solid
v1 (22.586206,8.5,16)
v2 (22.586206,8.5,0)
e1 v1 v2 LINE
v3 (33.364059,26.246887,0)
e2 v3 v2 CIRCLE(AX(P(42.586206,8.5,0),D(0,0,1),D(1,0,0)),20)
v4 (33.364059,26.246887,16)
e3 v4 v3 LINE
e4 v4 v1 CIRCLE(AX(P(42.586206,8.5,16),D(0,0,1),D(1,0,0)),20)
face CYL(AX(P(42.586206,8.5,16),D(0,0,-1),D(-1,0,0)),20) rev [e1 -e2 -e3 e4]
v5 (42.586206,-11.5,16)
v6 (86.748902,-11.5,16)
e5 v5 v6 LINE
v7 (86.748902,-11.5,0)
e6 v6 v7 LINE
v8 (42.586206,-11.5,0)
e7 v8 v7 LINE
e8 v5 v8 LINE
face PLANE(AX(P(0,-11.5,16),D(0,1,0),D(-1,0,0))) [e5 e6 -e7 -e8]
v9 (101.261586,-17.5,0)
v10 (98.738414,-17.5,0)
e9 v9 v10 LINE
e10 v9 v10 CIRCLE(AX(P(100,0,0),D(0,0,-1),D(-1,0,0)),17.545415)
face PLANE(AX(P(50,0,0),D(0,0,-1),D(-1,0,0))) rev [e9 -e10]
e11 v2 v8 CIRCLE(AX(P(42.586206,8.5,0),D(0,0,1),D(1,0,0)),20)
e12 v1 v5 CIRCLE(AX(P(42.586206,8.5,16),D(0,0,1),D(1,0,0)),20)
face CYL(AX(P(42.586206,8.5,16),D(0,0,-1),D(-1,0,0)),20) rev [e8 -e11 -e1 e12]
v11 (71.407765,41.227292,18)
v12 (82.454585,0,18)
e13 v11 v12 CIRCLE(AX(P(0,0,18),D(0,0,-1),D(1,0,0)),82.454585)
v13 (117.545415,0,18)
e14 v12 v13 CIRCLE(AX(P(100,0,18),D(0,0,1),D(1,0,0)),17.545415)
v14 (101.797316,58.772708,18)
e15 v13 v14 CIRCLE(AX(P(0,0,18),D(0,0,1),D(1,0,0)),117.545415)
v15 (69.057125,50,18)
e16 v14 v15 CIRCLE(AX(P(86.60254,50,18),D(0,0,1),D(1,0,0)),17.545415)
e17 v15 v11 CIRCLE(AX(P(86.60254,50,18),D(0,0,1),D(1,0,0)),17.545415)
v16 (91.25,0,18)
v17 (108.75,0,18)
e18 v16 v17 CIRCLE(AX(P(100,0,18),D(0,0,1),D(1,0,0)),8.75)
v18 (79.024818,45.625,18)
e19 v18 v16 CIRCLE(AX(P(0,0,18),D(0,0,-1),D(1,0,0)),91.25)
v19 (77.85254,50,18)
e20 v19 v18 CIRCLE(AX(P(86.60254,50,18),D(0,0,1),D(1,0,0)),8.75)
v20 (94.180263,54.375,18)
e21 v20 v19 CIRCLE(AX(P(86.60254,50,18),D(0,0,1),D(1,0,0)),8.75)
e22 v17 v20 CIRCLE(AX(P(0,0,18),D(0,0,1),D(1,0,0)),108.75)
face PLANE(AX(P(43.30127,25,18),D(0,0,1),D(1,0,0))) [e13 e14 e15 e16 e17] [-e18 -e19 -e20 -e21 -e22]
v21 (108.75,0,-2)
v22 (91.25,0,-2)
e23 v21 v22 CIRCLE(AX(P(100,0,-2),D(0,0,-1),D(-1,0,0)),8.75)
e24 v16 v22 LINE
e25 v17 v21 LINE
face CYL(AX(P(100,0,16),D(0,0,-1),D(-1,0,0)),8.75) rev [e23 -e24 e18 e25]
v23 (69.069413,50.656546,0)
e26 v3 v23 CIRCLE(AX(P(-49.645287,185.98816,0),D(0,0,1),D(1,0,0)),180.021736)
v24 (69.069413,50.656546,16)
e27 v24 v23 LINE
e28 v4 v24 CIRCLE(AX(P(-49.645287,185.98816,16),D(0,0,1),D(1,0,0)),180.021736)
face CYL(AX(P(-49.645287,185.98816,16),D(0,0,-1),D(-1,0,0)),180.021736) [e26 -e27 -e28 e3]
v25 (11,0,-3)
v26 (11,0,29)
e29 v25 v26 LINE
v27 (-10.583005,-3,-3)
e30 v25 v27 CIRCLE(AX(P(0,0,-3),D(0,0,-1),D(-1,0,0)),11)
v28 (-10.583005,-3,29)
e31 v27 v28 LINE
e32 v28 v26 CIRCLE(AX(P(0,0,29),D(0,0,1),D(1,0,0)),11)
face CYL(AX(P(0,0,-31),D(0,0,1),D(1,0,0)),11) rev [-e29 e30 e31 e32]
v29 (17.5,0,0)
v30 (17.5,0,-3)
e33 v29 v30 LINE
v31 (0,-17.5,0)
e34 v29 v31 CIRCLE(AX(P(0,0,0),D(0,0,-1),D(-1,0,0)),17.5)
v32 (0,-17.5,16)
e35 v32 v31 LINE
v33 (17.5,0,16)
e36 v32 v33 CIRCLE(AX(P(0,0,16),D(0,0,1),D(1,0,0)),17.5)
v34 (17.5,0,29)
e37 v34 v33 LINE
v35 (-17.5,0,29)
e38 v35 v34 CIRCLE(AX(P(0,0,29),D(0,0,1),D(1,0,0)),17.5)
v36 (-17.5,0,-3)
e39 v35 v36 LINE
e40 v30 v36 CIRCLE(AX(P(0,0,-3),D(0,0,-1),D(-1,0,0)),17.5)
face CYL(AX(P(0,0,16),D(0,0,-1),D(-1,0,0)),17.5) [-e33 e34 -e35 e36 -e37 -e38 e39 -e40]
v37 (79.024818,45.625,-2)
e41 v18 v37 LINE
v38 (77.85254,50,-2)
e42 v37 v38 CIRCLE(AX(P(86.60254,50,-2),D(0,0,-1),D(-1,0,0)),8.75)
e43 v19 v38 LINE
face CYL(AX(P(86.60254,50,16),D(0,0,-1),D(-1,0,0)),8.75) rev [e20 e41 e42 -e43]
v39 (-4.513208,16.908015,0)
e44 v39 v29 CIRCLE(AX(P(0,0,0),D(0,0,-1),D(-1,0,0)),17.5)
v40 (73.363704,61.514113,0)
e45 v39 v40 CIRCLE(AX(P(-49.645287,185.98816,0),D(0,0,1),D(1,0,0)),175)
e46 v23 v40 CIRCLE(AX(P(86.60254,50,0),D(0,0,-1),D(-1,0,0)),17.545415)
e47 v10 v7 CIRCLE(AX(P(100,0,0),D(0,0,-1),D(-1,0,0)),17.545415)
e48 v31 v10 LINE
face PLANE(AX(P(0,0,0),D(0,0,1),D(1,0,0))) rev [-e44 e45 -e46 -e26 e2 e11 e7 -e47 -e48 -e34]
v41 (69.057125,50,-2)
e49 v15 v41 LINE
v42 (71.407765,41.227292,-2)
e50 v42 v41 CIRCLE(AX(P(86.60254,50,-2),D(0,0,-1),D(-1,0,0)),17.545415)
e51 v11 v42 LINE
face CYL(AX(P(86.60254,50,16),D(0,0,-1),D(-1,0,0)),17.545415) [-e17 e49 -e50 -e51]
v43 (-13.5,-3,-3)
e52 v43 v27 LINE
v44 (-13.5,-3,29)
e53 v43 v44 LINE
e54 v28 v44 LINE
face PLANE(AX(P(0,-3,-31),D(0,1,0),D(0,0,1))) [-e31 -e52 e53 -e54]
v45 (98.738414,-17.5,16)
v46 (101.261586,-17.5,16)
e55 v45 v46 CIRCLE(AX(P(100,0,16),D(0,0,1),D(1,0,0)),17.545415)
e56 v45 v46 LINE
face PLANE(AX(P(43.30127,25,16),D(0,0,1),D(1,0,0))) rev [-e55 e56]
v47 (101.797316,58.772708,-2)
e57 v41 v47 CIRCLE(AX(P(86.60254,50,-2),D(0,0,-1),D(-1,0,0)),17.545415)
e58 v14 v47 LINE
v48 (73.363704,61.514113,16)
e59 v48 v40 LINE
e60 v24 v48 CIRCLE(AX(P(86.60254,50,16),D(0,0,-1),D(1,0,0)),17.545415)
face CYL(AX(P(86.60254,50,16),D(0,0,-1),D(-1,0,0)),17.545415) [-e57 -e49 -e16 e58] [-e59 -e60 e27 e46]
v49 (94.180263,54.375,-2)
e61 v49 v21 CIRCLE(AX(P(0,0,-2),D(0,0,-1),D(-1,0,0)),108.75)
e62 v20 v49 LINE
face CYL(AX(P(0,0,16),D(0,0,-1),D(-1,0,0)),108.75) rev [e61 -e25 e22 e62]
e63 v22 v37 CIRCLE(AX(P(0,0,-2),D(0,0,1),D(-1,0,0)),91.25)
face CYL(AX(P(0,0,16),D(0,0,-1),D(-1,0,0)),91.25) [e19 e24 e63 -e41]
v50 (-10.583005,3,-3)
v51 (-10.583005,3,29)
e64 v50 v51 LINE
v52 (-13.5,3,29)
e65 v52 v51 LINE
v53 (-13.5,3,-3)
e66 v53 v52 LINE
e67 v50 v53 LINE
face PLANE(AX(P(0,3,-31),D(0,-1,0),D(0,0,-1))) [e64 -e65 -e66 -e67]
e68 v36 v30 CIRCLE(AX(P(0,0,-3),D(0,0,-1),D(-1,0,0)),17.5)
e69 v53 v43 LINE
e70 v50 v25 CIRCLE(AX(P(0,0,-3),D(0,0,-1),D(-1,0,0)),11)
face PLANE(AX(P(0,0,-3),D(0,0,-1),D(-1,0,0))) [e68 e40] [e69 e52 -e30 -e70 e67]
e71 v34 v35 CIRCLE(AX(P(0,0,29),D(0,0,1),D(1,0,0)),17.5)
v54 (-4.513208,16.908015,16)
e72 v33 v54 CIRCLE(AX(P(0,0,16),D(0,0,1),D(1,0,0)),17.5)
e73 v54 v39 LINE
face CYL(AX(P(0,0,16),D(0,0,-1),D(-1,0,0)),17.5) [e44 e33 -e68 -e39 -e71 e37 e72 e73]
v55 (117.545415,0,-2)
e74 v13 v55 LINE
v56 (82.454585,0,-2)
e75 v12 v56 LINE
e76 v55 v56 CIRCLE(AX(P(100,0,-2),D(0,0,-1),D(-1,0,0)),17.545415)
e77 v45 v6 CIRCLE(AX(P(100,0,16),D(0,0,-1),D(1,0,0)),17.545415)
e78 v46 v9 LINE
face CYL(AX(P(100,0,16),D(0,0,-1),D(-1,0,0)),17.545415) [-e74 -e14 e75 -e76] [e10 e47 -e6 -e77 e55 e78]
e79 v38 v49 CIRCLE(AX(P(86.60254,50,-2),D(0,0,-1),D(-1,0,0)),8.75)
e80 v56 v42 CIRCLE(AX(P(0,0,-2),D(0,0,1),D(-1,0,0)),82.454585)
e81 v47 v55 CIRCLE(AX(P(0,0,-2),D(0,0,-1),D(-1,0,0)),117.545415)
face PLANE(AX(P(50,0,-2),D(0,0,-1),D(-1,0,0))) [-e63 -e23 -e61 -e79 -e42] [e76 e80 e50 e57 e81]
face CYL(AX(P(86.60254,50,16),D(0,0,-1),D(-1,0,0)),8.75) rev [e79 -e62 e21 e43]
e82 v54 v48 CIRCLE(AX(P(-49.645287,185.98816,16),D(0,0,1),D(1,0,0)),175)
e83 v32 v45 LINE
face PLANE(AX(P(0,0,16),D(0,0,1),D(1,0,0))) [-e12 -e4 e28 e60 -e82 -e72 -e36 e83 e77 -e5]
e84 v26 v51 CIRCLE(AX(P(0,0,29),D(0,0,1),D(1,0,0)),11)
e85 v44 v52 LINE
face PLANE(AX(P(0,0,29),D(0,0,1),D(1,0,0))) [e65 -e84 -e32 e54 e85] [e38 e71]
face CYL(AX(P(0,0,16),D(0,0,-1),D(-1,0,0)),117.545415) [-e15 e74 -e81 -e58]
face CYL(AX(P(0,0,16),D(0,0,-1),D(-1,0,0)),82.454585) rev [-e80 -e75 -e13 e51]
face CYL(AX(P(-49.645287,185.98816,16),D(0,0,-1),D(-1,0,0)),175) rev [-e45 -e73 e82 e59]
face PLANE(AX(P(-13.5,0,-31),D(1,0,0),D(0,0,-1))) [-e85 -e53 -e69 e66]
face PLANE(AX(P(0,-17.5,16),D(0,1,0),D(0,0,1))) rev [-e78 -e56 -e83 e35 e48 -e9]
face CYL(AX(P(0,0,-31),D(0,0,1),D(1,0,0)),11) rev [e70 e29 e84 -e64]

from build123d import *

# Parameters (mm, degrees)
LEVER_PLATE_16MM_DEPTH     = 16
HUB_FRONT_SKETCH_35_R      = 17.5
HUB_FRONT_BOSS_35X13_DEPTH = 13
HUB_START                  = 3
HUB_BACK_SKETCH_35_R       = 17.5
HUB_BACK_BOSS_35X3_DEPTH   = 3
KEYED_BORE_CUT_DEPTH       = 60
SLOT_RIM_A_2MM_DEPTH       = 2
SLOT_START                 = 2
SLOT_RIM_B_2MM_DEPTH       = 2


with BuildPart() as part:
    # Lever Profile Sketch → Lever Plate 16mm (new body)
    with BuildSketch(Plane.XY):
        with BuildLine():
            ThreePointArc((101.261586429, -17.5), (112.844778282, -11.952124129), (117.545415365, 0))
            ThreePointArc((117.545415365, 0), (113.540152463, 30.422992161), (101.797315804, 58.772707682))
            ThreePointArc((101.797315804, 58.772707682), (88.2863604, 67.464431009), (73.363703567, 61.514113087))
            ThreePointArc((73.363703567, 61.514113087), (37.333335855, 34.13389002), (-4.513207912, 16.9080145))
            ThreePointArc((-4.513207912, 16.9080145), (-17.351372478, -2.275933462), (0, -17.5))
            Line((0, -17.5), (101.261586429, -17.5))
        make_face()
        with BuildLine():
            ThreePointArc((71.407764953, 41.227292318), (79.645012795, 21.34081686), (82.454584635, 0))
            ThreePointArc((82.454584635, 0), (83.56318735, -6.137816406), (86.74890192, -11.5))
            Line((86.74890192, -11.5), (42.586205582, -11.5))
            ThreePointArc((42.586205582, -11.5), (23.157647429, 3.753303456), (33.364058597, 26.246887192))
            ThreePointArc((33.364058597, 26.246887192), (51.952476434, 37.375508628), (69.069413247, 50.656546497))
            ThreePointArc((69.069413247, 50.656546497), (69.572959936, 45.776850669), (71.407764953, 41.227292318))
        make_face(mode=Mode.SUBTRACT)
        with BuildLine():
            ThreePointArc((91.25, 0), (88.140731649, 23.617237866), (79.024818095, 45.625))
            ThreePointArc((79.024818095, 45.625), (82.227540378, 57.577722283), (94.180262662, 54.375))
            ThreePointArc((94.180262662, 54.375), (105.044433609, 28.146571155), (108.75, 0))
            ThreePointArc((108.75, 0), (100, -8.75), (91.25, 0))
        make_face(mode=Mode.SUBTRACT)
    extrude(amount=LEVER_PLATE_16MM_DEPTH)

    # Hub Front Sketch Ø35 → Hub Front Boss Ø35x13 (add)
    with BuildSketch(Plane.XY.offset(16)):
        with Locations(Location((0, 0, 0), (0, 0, 104.94534936))):
            Circle(HUB_FRONT_SKETCH_35_R)
    extrude(amount=HUB_FRONT_BOSS_35X13_DEPTH)

    # Hub Back Sketch Ø35 → Hub Back Boss Ø35x3 (add)
    with BuildSketch(Plane(origin=(0, 0, 0), x_dir=(-1, 0, 0), z_dir=(0, 0, -1)).offset(HUB_START)):
        Circle(HUB_BACK_SKETCH_35_R)
    extrude(amount=-HUB_BACK_BOSS_35X3_DEPTH)

    # Keyed Bore Sketch → Keyed Bore Cut (cut)
    with BuildSketch(Plane.XY.offset(29)):
        with BuildLine():
            ThreePointArc((-10.583005244, -3), (1.514421063, -10.895252583), (11, 0))
            Line((11, 0), (-13.5, 0))
            Line((-13.5, 0), (-13.5, -3))
            Line((-13.5, -3), (-10.583005244, -3))
        make_face()
        with BuildLine():
            Line((-13.5, 0), (11, 0))
            ThreePointArc((11, 0), (1.514421063, 10.895252583), (-10.583005244, 3))
            Line((-10.583005244, 3), (-13.5, 3))
            Line((-13.5, 3), (-13.5, 0))
        make_face()
    extrude(amount=-KEYED_BORE_CUT_DEPTH, mode=Mode.SUBTRACT)

    # Slot Rim Sketch A → Slot Rim A 2mm (add)
    with BuildSketch(Plane.XY.offset(16)):
        with BuildLine():
            ThreePointArc((117.545415365, 0), (113.540152463, 30.422992161), (101.797315804, 58.772707682))
            ThreePointArc((101.797315804, 58.772707682), (77.829832696, 65.194775426), (71.407764953, 41.227292318))
            ThreePointArc((71.407764953, 41.227292318), (79.645012795, 21.34081686), (82.454584635, 0))
            ThreePointArc((82.454584635, 0), (100, -17.545415365), (117.545415365, 0))
        make_face()
        with BuildLine():
            ThreePointArc((108.75, 0), (105.044433609, 28.146571155), (94.180262662, 54.375))
            ThreePointArc((94.180262662, 54.375), (82.227540378, 57.577722283), (79.024818095, 45.625))
            ThreePointArc((79.024818095, 45.625), (88.140731649, 23.617237866), (91.25, 0))
            ThreePointArc((91.25, 0), (100, -8.75), (108.75, 0))
        make_face(mode=Mode.SUBTRACT)
    extrude(amount=SLOT_RIM_A_2MM_DEPTH)

    # Slot Rim Sketch B → Slot Rim B 2mm (add)
    with BuildSketch(Plane(origin=(0, 0, 0), x_dir=(-1, 0, 0), z_dir=(0, 0, -1)).offset(SLOT_START)):
        with BuildLine():
            ThreePointArc((-101.797315804, 58.772707682), (-113.540152463, 30.422992161), (-117.545415365, 0))
            ThreePointArc((-117.545415365, 0), (-100, -17.545415365), (-82.454584635, 0))
            ThreePointArc((-82.454584635, 0), (-79.645012795, 21.34081686), (-71.407764953, 41.227292318))
            ThreePointArc((-71.407764953, 41.227292318), (-77.829832696, 65.194775426), (-101.797315804, 58.772707682))
        make_face()
        with BuildLine():
            ThreePointArc((-94.180262662, 54.375), (-105.044433609, 28.146571155), (-108.75, 0))
            ThreePointArc((-108.75, 0), (-100, -8.75), (-91.25, 0))
            ThreePointArc((-91.25, 0), (-88.140731649, 23.617237866), (-79.024818095, 45.625))
            ThreePointArc((-79.024818095, 45.625), (-82.227540378, 57.577722283), (-94.180262662, 54.375))
        make_face(mode=Mode.SUBTRACT)
    extrude(amount=-SLOT_RIM_B_2MM_DEPTH)


solid = part.part
